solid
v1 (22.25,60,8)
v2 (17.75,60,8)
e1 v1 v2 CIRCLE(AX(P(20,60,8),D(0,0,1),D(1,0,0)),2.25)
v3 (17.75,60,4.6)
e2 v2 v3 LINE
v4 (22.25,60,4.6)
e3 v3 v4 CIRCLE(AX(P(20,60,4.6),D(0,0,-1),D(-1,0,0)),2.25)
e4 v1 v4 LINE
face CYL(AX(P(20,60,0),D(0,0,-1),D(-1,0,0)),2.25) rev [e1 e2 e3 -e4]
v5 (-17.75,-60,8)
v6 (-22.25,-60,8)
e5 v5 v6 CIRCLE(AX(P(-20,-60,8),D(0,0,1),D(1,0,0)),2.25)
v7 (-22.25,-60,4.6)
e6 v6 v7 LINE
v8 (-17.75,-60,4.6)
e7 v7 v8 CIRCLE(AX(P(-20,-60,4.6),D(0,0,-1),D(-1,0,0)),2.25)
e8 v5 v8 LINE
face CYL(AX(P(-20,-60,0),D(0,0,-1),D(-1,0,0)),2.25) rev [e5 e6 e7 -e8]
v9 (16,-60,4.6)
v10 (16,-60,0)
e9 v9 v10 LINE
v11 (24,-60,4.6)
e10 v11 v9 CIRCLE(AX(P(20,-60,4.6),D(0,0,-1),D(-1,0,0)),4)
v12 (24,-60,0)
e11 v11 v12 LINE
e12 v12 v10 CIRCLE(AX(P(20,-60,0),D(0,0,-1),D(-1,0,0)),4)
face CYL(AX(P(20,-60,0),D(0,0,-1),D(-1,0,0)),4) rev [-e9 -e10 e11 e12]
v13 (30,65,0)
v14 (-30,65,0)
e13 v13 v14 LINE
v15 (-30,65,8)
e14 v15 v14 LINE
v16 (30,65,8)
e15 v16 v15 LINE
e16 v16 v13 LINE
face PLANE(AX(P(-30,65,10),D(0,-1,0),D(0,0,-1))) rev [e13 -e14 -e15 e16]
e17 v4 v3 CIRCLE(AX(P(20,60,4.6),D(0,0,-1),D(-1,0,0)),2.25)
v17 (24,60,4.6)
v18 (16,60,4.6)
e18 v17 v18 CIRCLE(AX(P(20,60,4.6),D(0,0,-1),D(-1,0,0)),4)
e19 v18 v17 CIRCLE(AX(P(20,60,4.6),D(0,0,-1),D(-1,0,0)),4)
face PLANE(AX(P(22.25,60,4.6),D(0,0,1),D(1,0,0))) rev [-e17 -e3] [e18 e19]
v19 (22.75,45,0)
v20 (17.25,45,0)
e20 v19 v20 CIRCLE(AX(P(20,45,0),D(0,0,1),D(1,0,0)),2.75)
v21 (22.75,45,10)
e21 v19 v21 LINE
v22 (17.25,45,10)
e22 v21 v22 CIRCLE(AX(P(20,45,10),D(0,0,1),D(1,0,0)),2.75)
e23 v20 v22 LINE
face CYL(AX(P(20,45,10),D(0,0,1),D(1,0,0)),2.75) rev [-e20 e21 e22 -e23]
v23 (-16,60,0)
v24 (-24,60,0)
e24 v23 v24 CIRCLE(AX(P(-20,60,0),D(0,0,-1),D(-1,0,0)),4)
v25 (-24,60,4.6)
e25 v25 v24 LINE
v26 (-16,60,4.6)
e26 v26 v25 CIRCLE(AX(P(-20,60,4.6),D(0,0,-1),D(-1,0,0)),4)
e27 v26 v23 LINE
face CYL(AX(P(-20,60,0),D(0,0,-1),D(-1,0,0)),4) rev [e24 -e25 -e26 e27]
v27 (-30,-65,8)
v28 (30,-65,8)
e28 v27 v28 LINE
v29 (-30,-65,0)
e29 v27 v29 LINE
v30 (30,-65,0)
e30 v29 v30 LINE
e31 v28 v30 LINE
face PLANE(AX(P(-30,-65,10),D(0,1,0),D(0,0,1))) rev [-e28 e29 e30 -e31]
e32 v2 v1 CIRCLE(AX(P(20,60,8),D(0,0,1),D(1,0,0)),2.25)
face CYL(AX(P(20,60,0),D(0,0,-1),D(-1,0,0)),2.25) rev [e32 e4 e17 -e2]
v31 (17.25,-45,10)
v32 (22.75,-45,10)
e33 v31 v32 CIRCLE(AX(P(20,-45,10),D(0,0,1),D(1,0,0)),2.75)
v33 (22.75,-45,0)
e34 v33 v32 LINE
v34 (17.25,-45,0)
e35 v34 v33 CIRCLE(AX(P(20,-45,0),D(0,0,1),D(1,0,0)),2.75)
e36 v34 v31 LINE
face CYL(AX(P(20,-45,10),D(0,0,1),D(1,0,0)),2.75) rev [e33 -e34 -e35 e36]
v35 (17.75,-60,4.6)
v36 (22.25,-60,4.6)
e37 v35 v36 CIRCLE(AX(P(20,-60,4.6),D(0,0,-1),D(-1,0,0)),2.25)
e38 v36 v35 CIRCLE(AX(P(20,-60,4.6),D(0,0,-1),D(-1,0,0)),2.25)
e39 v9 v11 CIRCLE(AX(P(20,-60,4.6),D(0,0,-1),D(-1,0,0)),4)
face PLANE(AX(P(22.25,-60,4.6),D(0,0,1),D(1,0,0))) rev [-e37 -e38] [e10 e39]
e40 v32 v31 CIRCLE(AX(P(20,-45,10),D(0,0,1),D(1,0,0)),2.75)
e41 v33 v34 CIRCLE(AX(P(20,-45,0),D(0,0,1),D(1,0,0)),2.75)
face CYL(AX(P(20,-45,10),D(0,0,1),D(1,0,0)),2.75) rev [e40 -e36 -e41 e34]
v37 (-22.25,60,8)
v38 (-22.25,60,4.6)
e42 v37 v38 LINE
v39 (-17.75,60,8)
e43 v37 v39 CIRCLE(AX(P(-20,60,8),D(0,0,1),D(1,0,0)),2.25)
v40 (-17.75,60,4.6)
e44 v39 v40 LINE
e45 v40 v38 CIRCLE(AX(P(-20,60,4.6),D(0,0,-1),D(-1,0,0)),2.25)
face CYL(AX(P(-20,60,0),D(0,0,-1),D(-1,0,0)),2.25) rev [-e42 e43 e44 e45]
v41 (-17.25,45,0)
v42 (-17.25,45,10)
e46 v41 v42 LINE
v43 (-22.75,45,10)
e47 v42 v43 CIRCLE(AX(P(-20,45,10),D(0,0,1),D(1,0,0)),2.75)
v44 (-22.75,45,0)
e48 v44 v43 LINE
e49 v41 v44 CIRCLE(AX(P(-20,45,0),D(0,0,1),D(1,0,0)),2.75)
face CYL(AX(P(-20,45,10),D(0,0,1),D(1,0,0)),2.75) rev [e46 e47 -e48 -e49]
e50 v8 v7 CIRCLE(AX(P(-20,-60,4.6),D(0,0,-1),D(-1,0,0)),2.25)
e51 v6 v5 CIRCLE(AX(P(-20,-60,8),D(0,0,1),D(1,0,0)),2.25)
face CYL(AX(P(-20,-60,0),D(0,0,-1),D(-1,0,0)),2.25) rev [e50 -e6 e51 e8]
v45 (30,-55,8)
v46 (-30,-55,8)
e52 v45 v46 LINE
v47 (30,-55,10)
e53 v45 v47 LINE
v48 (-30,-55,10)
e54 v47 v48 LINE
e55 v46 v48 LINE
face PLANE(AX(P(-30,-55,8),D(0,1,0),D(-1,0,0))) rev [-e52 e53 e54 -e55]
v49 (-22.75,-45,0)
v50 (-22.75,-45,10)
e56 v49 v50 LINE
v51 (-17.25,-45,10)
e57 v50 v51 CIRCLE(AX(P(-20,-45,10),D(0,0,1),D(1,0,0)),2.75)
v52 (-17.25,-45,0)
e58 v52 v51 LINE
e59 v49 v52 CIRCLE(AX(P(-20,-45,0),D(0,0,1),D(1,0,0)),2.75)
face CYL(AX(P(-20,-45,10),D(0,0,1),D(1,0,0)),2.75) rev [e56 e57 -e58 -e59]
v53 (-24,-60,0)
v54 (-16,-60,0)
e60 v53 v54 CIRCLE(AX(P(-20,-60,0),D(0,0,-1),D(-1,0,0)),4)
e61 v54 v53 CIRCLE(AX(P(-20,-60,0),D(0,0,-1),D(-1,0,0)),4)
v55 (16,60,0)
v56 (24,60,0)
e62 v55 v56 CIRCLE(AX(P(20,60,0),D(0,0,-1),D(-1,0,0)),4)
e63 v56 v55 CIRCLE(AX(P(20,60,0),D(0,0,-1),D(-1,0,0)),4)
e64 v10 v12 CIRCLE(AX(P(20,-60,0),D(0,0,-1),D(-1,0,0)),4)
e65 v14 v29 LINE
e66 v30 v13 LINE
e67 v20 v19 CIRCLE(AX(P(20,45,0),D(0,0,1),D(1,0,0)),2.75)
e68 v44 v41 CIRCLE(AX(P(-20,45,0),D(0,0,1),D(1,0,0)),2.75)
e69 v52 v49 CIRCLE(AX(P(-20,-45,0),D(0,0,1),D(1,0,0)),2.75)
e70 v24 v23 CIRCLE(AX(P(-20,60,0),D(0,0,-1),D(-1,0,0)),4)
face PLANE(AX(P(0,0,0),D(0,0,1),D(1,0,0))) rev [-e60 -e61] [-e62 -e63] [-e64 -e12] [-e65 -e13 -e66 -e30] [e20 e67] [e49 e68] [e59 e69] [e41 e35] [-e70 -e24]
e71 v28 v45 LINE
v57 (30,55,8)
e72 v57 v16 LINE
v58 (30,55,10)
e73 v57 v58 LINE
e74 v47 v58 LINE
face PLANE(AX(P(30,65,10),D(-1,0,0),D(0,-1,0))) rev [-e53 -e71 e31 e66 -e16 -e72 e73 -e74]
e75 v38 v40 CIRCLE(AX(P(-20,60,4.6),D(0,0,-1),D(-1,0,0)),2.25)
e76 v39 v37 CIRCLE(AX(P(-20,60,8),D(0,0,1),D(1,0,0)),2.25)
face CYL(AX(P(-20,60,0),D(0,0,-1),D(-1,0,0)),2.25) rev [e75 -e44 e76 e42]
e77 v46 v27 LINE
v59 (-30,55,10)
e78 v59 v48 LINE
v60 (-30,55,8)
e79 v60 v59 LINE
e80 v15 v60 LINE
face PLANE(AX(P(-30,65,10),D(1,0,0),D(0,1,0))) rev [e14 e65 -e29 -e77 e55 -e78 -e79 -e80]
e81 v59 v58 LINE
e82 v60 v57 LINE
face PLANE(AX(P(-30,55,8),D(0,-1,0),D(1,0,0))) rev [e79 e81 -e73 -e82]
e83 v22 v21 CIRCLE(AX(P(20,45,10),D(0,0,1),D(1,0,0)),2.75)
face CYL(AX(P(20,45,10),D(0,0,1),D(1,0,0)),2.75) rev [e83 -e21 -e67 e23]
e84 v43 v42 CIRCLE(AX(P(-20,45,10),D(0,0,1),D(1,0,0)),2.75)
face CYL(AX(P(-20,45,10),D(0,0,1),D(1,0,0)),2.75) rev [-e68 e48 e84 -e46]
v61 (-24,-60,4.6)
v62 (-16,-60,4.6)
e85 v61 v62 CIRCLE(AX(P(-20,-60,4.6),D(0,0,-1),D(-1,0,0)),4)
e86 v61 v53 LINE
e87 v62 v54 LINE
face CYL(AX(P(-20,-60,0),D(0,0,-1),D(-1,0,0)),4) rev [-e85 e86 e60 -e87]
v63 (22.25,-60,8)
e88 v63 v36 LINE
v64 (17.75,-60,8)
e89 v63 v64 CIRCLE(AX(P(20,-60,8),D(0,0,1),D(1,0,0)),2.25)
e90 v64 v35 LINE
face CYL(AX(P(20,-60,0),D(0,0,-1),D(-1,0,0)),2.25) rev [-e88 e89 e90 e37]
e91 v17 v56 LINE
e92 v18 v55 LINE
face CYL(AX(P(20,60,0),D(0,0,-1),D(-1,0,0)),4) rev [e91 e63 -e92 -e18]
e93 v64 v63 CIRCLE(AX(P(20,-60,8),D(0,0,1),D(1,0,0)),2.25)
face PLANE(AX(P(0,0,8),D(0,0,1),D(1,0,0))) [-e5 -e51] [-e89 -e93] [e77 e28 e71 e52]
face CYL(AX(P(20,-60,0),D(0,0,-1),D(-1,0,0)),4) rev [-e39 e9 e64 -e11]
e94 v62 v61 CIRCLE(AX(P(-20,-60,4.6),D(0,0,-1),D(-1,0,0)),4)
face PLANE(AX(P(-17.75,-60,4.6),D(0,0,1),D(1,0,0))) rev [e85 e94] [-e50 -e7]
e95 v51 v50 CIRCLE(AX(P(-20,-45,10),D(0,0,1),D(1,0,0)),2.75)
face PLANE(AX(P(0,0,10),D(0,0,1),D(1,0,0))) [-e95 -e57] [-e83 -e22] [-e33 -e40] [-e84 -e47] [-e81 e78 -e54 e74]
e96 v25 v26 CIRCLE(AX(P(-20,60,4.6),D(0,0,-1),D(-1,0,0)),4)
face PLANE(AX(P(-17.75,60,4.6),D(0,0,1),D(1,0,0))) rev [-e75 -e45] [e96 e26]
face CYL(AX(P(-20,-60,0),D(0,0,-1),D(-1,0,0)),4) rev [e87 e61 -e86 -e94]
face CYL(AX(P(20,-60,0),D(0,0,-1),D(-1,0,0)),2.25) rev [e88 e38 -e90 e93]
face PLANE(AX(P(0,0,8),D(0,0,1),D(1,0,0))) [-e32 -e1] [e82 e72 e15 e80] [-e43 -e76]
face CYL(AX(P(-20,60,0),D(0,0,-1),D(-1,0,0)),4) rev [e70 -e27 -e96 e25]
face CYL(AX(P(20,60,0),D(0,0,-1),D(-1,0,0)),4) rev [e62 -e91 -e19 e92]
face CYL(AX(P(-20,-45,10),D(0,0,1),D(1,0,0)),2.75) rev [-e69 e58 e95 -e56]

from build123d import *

# Parameters (mm, degrees)
SKETCH1_W                                           = 60
SKETCH1_H                                           = 130
BOSS_EXTRUDE1_DEPTH                                 = 10
SKETCH2_W                                           = 60
SKETCH2_H                                           = 10
CUT_EXTRUDE1_DEPTH                                  = 2
HOLE_SIZE_BY_SOCKET_HEAD_CAP_SCREW_TYPE_D           = 4.5
HOLE_SIZE_BY_SOCKET_HEAD_CAP_SCREW_TYPE_CBORE_D     = 8
HOLE_SIZE_BY_SOCKET_HEAD_CAP_SCREW_TYPE_CBORE_DEPTH = 4.6
M5_CLEARANCE_HOLE1_D                                = 5.5
M5_CLEARANCE_HOLE1_DEPTH                            = 15
M5_CLEARANCE_HOLE1_TIP                              = 1.652366702


with BuildPart() as part:
    # Sketch1 → Boss-Extrude1 (new body)
    with BuildSketch(Plane.XY):
        Rectangle(SKETCH1_W, SKETCH1_H)
    extrude(amount=BOSS_EXTRUDE1_DEPTH)

    # Sketch2 → Cut-Extrude1 (cut)
    with BuildSketch(Plane.XY.offset(10)):
        with Locations((0, 60)):
            Rectangle(SKETCH2_W, SKETCH2_H)
        with Locations((0, -60)):
            Rectangle(SKETCH2_W, SKETCH2_H)
    extrude(amount=-CUT_EXTRUDE1_DEPTH, mode=Mode.SUBTRACT)

    # Hole Size by Socket Head Cap Screw Type 1 (through all)
    with Locations(Plane(origin=(0, 0, 0), x_dir=(-1, 0, 0), z_dir=(0, 0, -1))):
        with Locations((20, -60), (-20, -60), (20, 60), (-20, 60)):
            CounterBoreHole(HOLE_SIZE_BY_SOCKET_HEAD_CAP_SCREW_TYPE_D / 2, HOLE_SIZE_BY_SOCKET_HEAD_CAP_SCREW_TYPE_CBORE_D / 2, HOLE_SIZE_BY_SOCKET_HEAD_CAP_SCREW_TYPE_CBORE_DEPTH)

    # M5 Clearance Hole1
    with Locations(Plane.XY.offset(10)):
        with Locations((-20, -45), (20, 45), (20, -45), (-20, 45)):
            Hole(M5_CLEARANCE_HOLE1_D / 2, depth=M5_CLEARANCE_HOLE1_DEPTH)
            with Locations((0, 0, -(M5_CLEARANCE_HOLE1_DEPTH + M5_CLEARANCE_HOLE1_TIP / 2))):  # 118° drill point
                Cone(0, M5_CLEARANCE_HOLE1_D / 2, M5_CLEARANCE_HOLE1_TIP, mode=Mode.SUBTRACT)


solid = part.part
